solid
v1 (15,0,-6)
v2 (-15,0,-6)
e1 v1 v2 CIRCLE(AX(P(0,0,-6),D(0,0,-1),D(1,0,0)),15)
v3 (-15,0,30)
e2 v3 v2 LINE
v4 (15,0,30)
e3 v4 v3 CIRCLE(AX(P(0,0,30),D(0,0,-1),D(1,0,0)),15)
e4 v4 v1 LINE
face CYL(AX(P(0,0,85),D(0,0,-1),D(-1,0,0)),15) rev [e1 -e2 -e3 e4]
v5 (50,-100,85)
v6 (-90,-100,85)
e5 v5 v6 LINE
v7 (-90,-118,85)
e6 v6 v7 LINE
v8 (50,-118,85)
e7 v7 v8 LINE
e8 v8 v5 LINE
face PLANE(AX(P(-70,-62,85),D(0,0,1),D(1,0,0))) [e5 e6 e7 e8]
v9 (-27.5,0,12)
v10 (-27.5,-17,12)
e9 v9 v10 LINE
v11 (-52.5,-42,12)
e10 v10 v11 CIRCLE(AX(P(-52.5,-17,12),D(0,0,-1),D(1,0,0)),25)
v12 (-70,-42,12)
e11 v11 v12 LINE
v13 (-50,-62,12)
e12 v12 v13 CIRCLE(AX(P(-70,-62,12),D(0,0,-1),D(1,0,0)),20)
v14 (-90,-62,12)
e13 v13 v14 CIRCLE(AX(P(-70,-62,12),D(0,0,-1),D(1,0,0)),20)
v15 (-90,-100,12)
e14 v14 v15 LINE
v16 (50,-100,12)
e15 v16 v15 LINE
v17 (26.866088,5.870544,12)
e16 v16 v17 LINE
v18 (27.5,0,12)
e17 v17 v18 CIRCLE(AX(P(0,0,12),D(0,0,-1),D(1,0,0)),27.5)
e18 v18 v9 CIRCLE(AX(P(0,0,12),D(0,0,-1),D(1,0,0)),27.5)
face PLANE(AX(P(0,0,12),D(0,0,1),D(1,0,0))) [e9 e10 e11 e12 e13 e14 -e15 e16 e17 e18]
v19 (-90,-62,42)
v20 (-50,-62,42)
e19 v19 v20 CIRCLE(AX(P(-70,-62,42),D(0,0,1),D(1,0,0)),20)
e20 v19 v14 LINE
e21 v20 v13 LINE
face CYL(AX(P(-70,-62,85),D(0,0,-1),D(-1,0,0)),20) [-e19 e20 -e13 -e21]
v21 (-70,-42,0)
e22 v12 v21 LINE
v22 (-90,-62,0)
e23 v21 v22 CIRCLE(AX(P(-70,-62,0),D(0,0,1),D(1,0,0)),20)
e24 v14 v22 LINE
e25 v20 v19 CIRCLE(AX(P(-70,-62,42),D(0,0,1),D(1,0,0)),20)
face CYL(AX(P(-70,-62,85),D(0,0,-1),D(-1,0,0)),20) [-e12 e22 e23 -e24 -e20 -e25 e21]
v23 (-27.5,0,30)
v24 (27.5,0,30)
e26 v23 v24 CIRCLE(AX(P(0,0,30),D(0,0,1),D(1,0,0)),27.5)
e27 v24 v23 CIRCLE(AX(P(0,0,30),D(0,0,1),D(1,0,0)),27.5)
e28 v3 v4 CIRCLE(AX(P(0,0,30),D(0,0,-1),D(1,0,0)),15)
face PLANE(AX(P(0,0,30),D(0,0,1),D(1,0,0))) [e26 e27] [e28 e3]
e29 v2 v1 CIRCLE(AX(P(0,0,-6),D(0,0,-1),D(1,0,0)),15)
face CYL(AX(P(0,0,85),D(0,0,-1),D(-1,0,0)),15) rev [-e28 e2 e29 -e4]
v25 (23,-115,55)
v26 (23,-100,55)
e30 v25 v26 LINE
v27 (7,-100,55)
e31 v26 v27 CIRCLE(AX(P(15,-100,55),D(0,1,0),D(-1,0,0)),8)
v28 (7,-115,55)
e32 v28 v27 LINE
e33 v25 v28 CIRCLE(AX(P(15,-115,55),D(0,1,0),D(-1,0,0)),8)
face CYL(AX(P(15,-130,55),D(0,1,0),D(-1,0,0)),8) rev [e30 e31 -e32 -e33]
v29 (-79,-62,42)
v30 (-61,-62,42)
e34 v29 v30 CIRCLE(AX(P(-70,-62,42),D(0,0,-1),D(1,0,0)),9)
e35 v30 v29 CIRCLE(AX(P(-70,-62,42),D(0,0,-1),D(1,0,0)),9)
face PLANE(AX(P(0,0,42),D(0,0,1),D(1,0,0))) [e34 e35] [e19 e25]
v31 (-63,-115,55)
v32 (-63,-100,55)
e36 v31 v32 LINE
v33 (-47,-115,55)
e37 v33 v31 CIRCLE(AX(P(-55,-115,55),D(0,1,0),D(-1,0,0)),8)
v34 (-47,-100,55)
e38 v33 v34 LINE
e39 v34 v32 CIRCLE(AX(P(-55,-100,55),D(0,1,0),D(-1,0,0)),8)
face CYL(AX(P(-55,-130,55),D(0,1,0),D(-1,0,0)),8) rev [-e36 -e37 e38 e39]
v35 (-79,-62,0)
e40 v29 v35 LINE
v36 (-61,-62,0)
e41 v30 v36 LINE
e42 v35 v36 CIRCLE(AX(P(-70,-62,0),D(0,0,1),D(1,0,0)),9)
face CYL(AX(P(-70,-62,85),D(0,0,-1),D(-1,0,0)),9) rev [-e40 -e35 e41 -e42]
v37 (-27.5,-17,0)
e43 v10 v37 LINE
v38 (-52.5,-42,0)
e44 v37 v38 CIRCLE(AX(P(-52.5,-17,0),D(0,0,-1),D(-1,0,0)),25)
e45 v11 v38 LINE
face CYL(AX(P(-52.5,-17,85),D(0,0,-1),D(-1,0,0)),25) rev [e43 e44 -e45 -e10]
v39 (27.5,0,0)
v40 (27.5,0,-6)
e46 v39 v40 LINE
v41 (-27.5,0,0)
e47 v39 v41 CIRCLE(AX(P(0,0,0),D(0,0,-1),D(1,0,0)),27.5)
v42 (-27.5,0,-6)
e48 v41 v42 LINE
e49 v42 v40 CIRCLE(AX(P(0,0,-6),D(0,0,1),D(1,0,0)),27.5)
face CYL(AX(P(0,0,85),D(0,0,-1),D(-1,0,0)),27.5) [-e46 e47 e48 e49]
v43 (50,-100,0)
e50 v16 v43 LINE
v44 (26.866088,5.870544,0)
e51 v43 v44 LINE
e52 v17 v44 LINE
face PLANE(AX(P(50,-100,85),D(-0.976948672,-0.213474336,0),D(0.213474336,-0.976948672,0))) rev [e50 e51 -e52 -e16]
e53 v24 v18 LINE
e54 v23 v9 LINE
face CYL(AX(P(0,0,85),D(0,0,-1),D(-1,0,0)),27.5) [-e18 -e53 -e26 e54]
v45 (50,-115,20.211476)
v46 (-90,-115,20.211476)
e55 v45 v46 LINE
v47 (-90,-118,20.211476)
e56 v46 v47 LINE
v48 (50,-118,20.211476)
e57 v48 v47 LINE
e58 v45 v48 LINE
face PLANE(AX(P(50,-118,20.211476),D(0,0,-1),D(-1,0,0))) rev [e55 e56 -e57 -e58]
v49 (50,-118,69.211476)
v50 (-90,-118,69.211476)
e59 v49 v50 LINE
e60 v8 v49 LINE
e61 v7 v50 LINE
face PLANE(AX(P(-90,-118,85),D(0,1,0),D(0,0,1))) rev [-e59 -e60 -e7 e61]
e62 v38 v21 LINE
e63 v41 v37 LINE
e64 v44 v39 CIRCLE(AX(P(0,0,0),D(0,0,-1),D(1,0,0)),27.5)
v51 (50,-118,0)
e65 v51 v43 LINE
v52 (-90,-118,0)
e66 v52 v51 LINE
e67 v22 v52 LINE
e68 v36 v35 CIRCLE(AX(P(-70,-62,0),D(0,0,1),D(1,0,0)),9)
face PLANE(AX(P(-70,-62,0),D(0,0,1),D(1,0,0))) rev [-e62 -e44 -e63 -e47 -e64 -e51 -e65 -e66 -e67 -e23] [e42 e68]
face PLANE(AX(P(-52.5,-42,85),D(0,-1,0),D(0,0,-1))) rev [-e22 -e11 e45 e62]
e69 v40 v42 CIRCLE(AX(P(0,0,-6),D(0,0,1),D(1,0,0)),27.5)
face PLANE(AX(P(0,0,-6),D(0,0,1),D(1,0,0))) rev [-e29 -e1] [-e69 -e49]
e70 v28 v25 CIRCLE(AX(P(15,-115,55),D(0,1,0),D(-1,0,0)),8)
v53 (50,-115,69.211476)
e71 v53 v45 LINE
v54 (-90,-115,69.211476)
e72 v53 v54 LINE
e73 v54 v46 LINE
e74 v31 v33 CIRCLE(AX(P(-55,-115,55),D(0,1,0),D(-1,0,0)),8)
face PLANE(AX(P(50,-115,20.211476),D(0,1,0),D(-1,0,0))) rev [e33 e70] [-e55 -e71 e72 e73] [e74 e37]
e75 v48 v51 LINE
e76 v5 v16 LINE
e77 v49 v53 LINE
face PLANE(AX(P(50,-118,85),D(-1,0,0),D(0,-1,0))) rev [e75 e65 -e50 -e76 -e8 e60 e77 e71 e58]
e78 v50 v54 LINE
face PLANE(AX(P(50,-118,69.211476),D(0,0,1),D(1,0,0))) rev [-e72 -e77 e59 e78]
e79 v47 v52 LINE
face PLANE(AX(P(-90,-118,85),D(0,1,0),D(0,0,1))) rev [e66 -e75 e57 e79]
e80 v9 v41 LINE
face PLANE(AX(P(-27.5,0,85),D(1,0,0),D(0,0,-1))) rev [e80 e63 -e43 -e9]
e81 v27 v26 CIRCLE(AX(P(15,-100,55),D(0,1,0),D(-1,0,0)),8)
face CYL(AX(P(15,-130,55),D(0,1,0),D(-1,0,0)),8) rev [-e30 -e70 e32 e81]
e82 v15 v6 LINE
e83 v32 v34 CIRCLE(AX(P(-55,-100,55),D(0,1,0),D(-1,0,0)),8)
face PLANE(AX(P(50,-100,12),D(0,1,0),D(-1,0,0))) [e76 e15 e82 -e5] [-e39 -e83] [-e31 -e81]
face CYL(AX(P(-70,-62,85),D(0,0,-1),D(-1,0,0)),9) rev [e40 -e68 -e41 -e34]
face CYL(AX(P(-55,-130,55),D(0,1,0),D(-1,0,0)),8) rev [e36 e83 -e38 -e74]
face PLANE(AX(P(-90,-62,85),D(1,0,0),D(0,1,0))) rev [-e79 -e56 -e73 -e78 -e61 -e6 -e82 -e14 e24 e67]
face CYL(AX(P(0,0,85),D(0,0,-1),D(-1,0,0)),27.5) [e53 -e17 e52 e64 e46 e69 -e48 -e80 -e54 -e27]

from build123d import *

# Parameters (mm, degrees)
BRACKET_PROFILE_SKETCH_R   = 15
BRACKET_PROFILE_SKETCH_R_2 = 9
BRACKET_BODY_DEPTH         = 85
GUSSET_TRIM_SKETCH_W       = 152.495630812
GUSSET_TRIM_SKETCH_H       = 155.202581702
GUSSET_TRIM_CUT_DEPTH      = 73
BASE_GROOVE_SKETCH_W       = 49
BASE_GROOVE_SKETCH_H       = 3
BASE_GROOVE_DEPTH          = 202.86381548
PIVOT_BOSSES_SKETCH_R      = 15
PIVOT_BOSS_36MM_DEPTH      = 18
SKETCH13_3_R               = 9
PIVOT_BOSS_30MM_DEPTH      = 30
MOUNTING_HOLES_SKETCH_R    = 8
BASE_MOUNTING_HOLES_DEPTH  = 30


with BuildPart() as part:
    # Bracket Profile Sketch → Bracket Body (new body)
    with BuildSketch(Plane.XY):
        with BuildLine():
            Line((-90, -62), (-90, -118))
            Line((-90, -118), (50, -118))
            Line((50, -118), (50, -100))
            Line((50, -100), (26.866088482, 5.870544241))
            ThreePointArc((26.866088482, 5.870544241), (-2.952335241, 27.341062829), (-27.5, 0))
            Line((-27.5, 0), (-27.5, -17))
            ThreePointArc((-27.5, -17), (-34.82233047, -34.67766953), (-52.5, -42))
            Line((-52.5, -42), (-70, -42))
            ThreePointArc((-70, -42), (-84.142135624, -47.857864376), (-90, -62))
        make_face()
        Circle(BRACKET_PROFILE_SKETCH_R, mode=Mode.SUBTRACT)
        with Locations((-70, -62)):
            Circle(BRACKET_PROFILE_SKETCH_R_2, mode=Mode.SUBTRACT)
    extrude(amount=BRACKET_BODY_DEPTH)

    # Gusset Trim Sketch → Gusset Trim Cut (cut)
    with BuildSketch(Plane.XY.offset(85)):
        with Locations((-26.247815406, -22.398709149)):
            Rectangle(GUSSET_TRIM_SKETCH_W, GUSSET_TRIM_SKETCH_H)
    extrude(amount=-GUSSET_TRIM_CUT_DEPTH, mode=Mode.SUBTRACT)

    # Base Groove Sketch → Base Groove (cut, through all)
    with BuildSketch(Plane.ZY.offset(90)):
        with Locations((44.711476451, -116.5)):
            Rectangle(BASE_GROOVE_SKETCH_W, BASE_GROOVE_SKETCH_H)
    extrude(amount=-BASE_GROOVE_DEPTH, mode=Mode.SUBTRACT)

    # Pivot Bosses Sketch → Pivot Boss 36mm (add, symmetric)
    with BuildSketch(Plane.XY.offset(12)):
        with BuildLine():
            ThreePointArc((-27.5, 0), (0, -27.5), (27.5, 0))
            ThreePointArc((27.5, 0), (27.341062829, 2.952335241), (26.866088482, 5.870544241))
            ThreePointArc((26.866088482, 5.870544241), (-2.952335241, 27.341062829), (-27.5, 0))
        make_face()
        Circle(PIVOT_BOSSES_SKETCH_R, mode=Mode.SUBTRACT)
    extrude(amount=PIVOT_BOSS_36MM_DEPTH, both=True)

    # Sketch13_3 → Pivot Boss 30mm (add)
    with BuildSketch(Plane.XY.offset(12)):
        with BuildLine():
            ThreePointArc((-90, -62), (-70, -82), (-50, -62))
            ThreePointArc((-50, -62), (-55.857864376, -47.857864376), (-70, -42))
            ThreePointArc((-70, -42), (-84.142135624, -47.857864376), (-90, -62))
        make_face()
        with Locations((-70, -62)):
            Circle(SKETCH13_3_R, mode=Mode.SUBTRACT)
    extrude(amount=PIVOT_BOSS_30MM_DEPTH)

    # Mounting Holes Sketch → Base Mounting Holes (cut)
    with BuildSketch(Plane(origin=(0, -100, 0), x_dir=(1, 0, 0), z_dir=(0, 1, 0))):
        with Locations(Location((-55, -55, 0), (0, 0, 180))):
            Circle(MOUNTING_HOLES_SKETCH_R)
        with Locations(Location((15, -55, 0), (0, 0, 180))):
            Circle(MOUNTING_HOLES_SKETCH_R)
    extrude(amount=-BASE_MOUNTING_HOLES_DEPTH, mode=Mode.SUBTRACT)


solid = part.part
